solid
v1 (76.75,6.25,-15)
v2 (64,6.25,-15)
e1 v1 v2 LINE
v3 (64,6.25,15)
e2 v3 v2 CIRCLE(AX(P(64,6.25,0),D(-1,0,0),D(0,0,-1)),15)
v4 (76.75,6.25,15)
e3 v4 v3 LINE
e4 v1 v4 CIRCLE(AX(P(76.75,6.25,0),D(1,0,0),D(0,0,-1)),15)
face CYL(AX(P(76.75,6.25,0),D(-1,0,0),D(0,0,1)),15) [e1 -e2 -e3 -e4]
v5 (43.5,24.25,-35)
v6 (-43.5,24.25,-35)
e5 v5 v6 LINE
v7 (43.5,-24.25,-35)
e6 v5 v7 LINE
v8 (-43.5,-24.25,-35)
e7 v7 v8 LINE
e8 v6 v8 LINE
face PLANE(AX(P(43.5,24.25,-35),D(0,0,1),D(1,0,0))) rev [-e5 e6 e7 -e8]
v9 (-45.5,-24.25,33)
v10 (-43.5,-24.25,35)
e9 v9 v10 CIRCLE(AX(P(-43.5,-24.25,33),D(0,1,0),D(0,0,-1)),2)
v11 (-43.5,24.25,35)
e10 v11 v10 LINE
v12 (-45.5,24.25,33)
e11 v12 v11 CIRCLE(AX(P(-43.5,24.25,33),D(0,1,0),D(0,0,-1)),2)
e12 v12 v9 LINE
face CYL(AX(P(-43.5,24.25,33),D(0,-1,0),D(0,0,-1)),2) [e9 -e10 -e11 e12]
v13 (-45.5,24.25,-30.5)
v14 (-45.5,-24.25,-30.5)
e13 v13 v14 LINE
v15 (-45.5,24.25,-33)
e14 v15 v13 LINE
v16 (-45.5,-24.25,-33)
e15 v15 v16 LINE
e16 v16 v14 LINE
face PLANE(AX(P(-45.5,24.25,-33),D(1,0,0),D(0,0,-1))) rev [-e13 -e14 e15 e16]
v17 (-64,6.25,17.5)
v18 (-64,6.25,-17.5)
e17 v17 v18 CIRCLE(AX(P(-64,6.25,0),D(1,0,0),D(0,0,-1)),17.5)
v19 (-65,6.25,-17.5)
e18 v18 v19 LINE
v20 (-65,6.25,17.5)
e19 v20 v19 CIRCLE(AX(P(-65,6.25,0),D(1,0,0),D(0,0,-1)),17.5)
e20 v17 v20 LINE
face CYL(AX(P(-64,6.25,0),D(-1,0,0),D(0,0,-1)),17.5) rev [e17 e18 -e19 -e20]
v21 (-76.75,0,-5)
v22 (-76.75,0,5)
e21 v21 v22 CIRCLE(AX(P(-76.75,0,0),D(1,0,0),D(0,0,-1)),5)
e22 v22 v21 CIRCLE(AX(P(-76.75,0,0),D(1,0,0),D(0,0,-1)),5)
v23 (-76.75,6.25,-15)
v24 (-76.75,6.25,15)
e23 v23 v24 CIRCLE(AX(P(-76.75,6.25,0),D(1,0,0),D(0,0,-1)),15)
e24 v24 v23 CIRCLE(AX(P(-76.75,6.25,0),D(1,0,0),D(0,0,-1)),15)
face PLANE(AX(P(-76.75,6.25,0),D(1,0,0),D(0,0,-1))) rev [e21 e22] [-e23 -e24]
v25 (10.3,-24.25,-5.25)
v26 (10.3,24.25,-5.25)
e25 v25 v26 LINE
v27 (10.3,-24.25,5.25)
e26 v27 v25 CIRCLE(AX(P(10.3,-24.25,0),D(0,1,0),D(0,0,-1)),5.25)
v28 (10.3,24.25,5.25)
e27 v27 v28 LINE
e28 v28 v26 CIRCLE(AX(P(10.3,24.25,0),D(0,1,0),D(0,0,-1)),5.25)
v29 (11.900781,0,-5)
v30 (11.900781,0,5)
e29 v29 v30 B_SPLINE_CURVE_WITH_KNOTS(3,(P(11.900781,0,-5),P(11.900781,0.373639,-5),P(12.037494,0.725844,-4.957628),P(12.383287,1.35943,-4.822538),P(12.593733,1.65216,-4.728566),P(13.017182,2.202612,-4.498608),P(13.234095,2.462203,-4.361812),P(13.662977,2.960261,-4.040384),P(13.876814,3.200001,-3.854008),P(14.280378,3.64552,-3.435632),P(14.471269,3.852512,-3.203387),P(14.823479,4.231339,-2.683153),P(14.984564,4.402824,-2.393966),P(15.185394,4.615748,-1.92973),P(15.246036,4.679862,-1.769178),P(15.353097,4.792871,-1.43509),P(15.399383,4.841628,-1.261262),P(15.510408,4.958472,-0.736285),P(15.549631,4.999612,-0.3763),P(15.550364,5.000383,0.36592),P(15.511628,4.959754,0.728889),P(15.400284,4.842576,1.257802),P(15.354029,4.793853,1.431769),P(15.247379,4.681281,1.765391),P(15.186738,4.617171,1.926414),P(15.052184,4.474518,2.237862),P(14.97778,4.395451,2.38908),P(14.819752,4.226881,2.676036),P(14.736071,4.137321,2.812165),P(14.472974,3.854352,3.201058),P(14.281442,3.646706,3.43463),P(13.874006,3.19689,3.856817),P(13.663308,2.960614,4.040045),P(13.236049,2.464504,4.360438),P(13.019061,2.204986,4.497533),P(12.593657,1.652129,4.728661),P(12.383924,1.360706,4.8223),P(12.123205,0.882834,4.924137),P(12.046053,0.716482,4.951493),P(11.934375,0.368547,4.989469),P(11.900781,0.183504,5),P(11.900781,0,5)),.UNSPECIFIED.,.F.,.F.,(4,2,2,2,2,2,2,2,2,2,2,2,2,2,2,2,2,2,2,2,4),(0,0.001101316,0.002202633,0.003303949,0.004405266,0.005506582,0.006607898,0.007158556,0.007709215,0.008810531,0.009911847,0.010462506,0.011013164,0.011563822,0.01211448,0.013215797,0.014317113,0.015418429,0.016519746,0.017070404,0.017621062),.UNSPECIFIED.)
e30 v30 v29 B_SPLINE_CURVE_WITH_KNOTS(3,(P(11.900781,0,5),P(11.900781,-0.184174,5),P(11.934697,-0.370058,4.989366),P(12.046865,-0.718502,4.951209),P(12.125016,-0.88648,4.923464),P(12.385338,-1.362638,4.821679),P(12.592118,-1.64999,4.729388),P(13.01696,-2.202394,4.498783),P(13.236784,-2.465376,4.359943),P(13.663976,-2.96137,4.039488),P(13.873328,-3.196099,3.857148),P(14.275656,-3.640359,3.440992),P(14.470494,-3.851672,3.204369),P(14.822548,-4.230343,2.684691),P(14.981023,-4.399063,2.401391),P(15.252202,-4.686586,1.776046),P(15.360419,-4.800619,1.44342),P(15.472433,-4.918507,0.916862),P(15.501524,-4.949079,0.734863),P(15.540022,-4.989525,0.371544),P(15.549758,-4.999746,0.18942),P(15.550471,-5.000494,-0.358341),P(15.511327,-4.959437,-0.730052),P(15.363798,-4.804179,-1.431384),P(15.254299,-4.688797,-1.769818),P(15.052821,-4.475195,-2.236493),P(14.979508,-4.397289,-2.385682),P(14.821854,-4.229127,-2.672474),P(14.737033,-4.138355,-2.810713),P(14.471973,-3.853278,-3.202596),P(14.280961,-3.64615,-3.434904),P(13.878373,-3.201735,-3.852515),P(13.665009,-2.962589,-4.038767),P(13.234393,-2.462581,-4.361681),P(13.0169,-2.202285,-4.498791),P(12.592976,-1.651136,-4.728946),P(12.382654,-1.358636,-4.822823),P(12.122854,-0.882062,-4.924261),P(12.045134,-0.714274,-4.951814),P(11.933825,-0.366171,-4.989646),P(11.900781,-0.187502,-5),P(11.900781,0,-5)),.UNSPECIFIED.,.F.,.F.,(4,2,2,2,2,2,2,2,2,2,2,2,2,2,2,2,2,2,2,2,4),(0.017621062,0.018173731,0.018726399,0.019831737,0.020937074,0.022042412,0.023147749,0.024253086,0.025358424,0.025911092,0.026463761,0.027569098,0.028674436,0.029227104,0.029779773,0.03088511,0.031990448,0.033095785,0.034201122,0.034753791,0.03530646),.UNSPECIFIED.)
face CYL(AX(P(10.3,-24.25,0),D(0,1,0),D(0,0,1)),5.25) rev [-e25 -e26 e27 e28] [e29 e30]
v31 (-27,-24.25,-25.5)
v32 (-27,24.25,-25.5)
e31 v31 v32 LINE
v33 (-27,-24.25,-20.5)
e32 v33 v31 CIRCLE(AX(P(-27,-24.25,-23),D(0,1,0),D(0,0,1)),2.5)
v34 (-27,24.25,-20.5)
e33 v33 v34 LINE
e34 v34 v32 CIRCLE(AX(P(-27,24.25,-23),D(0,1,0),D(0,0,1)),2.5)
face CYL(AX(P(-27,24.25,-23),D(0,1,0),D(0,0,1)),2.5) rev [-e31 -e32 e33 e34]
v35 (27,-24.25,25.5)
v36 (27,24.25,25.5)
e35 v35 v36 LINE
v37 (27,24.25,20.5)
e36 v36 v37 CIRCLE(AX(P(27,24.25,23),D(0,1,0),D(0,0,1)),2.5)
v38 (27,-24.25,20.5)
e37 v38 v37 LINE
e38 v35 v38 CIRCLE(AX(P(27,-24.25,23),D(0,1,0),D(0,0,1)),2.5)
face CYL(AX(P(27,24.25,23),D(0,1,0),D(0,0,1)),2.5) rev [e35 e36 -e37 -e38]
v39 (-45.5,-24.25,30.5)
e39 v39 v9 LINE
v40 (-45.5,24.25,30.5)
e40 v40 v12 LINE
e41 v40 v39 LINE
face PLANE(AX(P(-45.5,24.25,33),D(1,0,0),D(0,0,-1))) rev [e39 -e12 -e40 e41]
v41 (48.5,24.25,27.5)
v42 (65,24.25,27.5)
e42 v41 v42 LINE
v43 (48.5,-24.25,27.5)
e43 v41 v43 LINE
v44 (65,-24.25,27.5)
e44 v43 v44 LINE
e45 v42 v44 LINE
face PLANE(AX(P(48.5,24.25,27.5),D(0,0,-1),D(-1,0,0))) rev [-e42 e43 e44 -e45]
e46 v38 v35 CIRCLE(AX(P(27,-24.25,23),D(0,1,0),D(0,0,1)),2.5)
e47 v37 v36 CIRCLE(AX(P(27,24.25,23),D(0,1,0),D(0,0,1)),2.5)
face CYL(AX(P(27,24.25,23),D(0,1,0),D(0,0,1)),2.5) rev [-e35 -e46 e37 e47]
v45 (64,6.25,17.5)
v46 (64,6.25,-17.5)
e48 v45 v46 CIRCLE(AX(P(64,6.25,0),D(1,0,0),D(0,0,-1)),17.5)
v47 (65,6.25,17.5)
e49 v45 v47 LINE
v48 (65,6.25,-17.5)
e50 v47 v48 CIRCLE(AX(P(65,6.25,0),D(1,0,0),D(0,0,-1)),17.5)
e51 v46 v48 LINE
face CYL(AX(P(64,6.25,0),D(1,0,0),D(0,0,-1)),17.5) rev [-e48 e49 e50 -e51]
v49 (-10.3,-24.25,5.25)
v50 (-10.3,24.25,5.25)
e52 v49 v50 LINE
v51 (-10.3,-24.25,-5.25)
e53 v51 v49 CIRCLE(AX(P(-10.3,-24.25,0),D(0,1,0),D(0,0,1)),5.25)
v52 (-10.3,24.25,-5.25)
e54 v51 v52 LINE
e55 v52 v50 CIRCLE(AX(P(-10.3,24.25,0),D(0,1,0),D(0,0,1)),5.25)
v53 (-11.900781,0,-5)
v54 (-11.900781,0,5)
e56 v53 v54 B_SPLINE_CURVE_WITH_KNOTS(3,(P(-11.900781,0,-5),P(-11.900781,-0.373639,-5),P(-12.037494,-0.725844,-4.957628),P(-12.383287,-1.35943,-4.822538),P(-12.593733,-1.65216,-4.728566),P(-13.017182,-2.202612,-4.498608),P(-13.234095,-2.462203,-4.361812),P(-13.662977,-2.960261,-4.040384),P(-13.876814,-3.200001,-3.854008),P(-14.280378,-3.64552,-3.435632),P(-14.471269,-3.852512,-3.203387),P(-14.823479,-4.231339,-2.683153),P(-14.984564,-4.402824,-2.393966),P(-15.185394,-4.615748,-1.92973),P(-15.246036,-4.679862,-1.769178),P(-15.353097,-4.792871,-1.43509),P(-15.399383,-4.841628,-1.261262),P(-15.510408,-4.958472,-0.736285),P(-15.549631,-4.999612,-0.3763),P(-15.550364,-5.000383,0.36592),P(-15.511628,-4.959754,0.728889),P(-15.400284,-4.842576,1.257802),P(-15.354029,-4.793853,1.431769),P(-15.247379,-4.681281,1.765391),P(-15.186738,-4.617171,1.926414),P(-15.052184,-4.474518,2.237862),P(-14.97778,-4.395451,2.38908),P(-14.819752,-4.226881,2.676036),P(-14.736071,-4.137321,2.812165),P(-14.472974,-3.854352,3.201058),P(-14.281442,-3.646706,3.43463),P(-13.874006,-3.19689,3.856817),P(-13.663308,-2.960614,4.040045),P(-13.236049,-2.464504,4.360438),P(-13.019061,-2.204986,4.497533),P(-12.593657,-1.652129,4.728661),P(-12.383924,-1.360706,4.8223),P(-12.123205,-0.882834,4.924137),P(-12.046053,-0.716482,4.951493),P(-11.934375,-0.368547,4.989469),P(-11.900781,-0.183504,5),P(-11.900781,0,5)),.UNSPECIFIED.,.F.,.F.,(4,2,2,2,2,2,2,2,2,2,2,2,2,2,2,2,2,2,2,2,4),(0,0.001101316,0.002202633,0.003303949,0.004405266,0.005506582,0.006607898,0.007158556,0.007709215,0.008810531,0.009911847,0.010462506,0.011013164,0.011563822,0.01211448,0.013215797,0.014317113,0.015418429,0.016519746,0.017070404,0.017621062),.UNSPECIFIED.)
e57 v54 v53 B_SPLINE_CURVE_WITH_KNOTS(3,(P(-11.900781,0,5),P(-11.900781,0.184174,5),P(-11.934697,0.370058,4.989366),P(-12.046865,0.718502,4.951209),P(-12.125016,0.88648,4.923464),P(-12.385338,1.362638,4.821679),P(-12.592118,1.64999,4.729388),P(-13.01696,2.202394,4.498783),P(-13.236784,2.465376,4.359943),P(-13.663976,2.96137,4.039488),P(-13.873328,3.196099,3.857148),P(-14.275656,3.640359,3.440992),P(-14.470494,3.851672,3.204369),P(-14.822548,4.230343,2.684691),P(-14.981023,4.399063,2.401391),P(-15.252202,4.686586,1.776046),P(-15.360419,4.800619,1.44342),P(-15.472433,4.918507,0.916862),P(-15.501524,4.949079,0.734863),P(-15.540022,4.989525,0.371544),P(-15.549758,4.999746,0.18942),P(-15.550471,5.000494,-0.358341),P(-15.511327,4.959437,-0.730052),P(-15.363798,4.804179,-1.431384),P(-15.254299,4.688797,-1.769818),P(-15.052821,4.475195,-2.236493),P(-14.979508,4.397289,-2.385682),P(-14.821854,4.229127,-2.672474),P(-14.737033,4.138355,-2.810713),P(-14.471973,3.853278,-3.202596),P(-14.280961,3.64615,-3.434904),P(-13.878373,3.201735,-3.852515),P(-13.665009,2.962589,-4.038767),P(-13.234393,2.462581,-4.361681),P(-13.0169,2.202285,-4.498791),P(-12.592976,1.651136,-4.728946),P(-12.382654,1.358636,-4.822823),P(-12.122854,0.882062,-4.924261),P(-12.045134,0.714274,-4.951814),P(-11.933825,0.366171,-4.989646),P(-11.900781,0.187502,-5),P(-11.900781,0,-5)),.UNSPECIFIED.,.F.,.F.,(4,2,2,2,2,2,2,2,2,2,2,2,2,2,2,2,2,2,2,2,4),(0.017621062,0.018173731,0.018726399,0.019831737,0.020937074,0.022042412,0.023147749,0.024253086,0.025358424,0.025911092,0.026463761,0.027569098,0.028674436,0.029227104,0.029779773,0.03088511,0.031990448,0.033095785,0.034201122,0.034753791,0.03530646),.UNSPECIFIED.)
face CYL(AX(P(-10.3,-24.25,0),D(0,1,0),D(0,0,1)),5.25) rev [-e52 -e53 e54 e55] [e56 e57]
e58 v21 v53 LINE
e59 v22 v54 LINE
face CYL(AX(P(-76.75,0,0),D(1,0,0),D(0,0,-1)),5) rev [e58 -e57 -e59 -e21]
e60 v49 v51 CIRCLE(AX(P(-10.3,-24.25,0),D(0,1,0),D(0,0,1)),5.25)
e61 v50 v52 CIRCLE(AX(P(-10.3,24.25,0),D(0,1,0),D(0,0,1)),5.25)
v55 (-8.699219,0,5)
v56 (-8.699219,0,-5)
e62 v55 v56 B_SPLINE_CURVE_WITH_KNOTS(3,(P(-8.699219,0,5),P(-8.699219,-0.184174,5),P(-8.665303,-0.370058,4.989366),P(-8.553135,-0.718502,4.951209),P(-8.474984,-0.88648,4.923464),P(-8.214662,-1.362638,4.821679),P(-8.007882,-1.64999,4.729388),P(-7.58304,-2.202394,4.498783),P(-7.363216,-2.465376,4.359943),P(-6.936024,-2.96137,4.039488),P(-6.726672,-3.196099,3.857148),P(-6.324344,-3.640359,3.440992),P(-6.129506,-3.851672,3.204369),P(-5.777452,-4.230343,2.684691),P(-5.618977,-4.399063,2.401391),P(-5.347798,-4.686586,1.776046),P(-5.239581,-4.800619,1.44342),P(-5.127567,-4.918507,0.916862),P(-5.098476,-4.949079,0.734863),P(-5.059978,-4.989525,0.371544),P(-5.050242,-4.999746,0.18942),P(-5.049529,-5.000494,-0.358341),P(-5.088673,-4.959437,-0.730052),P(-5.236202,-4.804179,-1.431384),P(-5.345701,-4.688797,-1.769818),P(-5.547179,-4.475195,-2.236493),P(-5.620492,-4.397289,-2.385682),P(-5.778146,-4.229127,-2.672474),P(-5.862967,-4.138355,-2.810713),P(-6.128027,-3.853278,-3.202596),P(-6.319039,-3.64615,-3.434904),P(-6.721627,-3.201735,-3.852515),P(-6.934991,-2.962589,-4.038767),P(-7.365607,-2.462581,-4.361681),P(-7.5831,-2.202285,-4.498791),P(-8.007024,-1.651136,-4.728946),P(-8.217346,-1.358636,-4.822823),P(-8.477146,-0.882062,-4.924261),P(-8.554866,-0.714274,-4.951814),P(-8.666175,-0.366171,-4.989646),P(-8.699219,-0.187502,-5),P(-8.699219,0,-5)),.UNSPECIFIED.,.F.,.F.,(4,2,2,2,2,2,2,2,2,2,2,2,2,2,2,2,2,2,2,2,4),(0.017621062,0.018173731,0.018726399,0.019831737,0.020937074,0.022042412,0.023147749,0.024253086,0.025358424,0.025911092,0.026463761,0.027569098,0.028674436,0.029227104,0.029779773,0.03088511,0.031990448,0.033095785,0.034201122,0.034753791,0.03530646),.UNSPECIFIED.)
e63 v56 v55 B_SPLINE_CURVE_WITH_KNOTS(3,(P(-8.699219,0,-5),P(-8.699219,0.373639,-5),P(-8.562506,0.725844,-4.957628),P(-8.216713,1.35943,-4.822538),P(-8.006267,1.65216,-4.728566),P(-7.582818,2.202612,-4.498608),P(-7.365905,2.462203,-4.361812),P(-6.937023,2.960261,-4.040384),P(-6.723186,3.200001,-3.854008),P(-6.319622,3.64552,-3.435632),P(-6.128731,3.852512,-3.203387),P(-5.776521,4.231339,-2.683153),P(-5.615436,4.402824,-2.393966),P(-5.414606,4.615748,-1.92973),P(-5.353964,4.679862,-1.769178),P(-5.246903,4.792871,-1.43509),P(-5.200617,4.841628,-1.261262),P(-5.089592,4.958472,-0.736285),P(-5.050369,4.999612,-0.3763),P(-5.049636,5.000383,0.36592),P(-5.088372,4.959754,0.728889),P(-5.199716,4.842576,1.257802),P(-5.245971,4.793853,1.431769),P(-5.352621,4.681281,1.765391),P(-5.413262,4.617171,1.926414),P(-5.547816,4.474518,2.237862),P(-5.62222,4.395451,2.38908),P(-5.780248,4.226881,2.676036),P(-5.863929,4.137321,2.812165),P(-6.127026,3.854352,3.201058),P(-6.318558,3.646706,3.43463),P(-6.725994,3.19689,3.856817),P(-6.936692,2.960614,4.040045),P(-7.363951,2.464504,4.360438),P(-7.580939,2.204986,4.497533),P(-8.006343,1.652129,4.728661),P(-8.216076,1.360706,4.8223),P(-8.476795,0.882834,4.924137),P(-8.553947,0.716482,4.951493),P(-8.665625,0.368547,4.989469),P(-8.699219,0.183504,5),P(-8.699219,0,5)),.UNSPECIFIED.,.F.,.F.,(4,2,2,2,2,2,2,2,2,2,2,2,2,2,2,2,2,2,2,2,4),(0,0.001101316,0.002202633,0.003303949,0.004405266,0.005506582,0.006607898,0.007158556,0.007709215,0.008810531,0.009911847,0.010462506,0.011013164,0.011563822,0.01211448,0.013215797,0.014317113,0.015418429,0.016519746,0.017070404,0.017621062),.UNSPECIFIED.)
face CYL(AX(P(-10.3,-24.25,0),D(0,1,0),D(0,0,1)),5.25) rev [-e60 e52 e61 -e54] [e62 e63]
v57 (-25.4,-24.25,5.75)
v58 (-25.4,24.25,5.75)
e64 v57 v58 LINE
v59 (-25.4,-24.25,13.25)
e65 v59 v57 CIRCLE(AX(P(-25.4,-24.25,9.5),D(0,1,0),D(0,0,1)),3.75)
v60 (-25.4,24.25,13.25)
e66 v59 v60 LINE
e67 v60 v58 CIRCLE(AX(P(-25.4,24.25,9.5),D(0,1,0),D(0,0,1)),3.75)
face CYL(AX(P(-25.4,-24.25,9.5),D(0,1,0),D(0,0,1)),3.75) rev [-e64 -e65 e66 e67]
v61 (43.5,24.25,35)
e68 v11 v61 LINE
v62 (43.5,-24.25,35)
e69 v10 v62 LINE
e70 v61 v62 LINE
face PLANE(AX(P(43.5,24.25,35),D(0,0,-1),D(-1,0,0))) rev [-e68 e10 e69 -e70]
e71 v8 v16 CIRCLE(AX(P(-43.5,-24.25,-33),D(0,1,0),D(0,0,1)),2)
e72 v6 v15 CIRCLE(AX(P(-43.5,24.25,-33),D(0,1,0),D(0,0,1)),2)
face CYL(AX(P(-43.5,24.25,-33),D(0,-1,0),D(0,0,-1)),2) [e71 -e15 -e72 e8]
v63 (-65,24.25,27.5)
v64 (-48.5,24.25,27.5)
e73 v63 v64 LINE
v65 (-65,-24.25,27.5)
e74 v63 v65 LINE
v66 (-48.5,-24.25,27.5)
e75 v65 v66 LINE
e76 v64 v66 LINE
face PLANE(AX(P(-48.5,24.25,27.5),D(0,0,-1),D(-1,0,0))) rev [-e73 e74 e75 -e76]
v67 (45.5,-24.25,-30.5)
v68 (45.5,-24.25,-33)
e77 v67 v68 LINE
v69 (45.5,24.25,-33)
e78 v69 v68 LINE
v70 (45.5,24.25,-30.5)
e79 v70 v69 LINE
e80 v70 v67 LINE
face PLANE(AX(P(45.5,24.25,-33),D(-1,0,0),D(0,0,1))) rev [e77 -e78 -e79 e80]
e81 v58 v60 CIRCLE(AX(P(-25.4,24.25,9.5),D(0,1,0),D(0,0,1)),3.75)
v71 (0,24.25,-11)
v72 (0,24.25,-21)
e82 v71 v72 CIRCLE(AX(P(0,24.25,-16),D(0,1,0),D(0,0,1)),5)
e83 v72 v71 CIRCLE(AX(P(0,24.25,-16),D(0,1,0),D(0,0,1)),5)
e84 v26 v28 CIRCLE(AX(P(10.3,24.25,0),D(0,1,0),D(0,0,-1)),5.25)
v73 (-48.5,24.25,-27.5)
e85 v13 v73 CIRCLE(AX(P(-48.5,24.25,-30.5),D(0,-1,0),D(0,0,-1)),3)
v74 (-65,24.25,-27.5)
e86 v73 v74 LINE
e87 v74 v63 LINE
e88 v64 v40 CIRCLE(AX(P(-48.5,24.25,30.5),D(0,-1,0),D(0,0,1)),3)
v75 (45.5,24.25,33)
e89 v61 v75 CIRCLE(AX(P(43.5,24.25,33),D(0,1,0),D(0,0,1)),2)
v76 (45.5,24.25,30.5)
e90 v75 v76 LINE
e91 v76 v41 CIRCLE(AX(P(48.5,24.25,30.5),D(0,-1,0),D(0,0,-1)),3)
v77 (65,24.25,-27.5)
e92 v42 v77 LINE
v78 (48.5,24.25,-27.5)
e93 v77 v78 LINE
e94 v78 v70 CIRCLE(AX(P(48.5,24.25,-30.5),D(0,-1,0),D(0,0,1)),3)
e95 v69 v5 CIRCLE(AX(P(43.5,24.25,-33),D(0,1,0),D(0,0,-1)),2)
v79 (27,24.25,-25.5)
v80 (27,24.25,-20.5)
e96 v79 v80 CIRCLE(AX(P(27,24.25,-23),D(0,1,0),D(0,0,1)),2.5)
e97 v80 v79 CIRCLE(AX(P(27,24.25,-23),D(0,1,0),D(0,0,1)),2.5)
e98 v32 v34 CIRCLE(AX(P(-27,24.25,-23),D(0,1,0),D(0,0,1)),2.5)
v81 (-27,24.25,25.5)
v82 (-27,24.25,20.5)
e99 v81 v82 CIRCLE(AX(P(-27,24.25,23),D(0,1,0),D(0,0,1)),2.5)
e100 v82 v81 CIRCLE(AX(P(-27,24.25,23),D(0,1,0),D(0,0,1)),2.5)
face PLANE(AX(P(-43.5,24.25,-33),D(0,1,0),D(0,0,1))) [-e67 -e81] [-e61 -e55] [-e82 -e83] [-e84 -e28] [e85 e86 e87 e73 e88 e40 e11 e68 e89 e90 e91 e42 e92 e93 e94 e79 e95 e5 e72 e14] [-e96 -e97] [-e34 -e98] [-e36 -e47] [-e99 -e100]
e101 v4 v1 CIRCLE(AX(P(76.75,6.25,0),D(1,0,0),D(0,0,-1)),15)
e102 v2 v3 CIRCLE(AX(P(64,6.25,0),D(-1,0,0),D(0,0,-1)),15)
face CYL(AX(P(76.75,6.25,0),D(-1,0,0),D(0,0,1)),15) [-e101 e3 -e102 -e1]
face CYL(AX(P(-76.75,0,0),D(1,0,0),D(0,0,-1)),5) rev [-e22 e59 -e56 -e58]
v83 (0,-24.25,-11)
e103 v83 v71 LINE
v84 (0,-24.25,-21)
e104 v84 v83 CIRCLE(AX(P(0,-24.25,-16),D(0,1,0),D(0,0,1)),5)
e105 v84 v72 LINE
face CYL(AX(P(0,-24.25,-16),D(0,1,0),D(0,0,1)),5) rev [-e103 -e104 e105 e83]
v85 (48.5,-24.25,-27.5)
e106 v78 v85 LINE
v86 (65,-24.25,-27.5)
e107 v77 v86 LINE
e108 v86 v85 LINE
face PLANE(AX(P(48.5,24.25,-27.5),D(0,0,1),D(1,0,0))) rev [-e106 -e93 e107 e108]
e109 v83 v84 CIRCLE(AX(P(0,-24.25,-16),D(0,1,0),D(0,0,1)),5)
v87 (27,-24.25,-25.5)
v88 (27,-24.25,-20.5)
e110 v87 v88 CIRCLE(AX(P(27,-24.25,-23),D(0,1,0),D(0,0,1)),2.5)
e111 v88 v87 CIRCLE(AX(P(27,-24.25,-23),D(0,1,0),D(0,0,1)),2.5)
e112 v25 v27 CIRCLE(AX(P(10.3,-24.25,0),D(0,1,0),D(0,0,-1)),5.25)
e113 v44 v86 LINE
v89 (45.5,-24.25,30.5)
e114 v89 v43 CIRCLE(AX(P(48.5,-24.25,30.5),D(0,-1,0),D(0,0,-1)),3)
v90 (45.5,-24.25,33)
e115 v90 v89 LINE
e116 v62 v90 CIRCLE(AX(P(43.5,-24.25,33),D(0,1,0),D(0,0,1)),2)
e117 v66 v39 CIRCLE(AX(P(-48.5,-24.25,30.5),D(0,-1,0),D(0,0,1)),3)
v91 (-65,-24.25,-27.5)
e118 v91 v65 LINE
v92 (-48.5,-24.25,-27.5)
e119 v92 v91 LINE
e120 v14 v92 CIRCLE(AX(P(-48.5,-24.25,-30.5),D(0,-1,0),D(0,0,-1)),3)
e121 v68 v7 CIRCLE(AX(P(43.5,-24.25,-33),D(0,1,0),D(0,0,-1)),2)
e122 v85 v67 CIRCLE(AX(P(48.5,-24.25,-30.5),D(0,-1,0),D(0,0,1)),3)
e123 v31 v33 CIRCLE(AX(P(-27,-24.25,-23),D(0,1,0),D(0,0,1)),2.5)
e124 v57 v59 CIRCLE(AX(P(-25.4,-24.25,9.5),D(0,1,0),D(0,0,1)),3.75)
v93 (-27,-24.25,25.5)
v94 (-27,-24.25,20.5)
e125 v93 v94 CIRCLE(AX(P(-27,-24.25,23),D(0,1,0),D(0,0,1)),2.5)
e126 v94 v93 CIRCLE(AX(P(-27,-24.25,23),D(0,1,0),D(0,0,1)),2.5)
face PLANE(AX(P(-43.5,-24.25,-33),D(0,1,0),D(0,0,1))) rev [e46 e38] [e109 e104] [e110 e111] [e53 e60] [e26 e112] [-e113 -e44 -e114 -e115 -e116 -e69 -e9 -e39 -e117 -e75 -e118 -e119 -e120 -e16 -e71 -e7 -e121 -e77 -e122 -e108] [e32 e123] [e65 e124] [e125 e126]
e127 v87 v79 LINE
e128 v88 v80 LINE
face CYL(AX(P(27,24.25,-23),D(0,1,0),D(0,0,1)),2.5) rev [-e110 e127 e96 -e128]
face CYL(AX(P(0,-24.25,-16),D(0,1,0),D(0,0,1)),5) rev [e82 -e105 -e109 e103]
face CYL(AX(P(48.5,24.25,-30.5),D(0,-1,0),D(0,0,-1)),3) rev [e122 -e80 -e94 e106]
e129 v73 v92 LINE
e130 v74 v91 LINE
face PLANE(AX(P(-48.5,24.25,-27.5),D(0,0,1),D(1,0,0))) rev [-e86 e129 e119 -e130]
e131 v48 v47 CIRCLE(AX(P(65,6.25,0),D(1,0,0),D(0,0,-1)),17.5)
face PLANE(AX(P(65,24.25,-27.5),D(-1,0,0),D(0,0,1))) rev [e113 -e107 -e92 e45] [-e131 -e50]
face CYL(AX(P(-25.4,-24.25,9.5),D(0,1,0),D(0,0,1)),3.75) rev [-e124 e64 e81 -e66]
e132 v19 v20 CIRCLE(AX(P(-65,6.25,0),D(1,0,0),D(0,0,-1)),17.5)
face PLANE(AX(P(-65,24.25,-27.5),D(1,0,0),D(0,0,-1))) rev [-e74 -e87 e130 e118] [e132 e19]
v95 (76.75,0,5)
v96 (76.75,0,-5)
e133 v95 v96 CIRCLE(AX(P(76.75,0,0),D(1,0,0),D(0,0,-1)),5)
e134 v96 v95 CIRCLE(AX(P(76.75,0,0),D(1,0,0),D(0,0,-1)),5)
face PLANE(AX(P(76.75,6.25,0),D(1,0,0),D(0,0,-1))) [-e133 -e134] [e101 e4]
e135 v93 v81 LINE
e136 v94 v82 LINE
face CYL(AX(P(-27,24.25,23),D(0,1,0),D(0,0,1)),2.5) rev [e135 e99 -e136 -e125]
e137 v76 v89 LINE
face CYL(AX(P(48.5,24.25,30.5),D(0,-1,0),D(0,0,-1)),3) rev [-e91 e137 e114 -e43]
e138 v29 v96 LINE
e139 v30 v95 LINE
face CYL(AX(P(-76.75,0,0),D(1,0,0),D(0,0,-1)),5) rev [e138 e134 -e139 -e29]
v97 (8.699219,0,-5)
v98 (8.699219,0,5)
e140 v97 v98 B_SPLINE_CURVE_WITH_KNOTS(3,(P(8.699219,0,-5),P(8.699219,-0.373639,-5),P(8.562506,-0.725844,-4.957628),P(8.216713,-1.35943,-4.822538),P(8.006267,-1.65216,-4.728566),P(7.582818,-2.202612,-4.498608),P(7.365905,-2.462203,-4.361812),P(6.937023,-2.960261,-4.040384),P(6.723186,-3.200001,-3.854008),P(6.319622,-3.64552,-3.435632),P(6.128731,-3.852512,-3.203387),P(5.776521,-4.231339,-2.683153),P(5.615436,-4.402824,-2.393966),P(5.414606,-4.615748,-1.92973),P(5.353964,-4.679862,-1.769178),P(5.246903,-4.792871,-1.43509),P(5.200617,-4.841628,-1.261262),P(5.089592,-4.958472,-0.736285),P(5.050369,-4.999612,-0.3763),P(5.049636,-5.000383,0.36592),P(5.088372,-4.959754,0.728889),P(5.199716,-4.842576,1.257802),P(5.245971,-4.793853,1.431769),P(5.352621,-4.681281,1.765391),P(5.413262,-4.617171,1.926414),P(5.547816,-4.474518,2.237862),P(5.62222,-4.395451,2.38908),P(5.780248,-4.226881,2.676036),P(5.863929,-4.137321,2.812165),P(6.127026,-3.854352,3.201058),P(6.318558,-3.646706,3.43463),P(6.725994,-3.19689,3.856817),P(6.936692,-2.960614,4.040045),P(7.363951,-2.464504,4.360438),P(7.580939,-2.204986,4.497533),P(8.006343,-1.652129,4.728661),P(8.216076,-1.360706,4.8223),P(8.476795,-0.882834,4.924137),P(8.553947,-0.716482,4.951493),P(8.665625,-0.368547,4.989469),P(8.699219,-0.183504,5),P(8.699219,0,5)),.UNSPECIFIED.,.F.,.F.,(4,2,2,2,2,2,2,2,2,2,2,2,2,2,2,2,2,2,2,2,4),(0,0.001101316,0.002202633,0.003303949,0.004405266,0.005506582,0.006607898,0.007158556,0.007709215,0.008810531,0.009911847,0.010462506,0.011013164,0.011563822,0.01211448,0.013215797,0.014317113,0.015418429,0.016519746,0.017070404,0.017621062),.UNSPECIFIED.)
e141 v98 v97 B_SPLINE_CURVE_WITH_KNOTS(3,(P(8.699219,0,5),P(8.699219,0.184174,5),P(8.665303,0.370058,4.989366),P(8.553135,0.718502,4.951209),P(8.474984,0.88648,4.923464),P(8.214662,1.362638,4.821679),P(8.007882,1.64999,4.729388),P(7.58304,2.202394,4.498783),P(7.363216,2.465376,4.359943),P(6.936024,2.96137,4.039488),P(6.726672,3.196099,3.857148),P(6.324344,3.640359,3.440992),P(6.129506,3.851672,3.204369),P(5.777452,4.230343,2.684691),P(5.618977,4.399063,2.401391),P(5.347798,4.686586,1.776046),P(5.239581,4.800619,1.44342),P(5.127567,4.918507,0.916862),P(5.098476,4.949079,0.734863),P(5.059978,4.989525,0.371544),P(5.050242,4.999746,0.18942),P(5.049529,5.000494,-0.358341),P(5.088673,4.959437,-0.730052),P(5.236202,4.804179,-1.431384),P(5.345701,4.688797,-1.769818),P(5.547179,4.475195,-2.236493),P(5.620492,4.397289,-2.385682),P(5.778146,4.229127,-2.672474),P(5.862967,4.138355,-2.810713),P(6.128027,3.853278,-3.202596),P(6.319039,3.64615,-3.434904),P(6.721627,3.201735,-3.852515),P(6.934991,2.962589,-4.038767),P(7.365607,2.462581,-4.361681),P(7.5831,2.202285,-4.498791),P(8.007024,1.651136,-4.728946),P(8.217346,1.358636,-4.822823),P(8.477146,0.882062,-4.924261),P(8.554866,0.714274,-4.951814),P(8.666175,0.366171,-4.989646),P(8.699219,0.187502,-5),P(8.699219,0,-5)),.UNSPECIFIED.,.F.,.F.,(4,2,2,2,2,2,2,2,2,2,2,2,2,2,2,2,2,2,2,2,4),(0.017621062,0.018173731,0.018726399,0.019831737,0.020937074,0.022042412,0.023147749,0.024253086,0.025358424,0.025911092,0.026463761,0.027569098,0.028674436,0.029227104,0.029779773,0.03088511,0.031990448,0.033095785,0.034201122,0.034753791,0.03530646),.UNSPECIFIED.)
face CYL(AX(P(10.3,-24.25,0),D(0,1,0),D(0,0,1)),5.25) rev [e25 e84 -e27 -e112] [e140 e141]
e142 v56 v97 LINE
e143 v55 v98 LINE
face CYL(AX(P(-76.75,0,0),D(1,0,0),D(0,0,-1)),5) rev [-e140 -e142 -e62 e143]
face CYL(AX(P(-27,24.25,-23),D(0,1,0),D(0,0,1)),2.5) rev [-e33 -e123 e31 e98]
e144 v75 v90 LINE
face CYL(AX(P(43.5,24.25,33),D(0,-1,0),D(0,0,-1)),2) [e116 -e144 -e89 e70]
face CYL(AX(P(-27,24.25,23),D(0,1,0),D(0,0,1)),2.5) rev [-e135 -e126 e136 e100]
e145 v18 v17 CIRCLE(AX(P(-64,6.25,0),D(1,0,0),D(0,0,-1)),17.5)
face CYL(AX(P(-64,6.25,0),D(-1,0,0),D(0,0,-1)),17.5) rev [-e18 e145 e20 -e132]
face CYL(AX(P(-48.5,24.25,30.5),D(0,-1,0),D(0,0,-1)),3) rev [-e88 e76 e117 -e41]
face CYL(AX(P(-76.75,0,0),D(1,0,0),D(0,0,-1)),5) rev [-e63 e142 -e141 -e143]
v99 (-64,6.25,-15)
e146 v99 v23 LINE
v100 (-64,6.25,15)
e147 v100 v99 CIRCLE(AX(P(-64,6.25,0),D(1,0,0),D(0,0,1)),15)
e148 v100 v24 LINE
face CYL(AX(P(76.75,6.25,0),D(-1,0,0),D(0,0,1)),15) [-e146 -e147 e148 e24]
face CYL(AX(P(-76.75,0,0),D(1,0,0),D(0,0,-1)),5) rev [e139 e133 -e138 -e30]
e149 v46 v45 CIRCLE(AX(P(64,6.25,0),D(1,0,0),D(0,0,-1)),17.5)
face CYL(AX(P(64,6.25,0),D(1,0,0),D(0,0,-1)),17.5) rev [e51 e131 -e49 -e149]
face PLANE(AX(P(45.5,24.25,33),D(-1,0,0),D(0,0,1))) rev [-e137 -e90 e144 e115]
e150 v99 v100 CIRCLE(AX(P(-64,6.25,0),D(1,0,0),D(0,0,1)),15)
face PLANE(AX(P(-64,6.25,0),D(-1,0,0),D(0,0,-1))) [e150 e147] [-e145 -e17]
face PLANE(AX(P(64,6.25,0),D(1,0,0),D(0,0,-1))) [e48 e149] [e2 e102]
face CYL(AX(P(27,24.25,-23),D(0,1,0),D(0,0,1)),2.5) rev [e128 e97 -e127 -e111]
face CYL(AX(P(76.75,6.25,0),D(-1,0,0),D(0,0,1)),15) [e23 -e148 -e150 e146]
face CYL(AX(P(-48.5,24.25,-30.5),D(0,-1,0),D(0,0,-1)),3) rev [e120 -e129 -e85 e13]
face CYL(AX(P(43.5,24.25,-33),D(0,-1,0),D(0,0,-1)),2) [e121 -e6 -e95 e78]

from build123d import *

# Parameters (mm, degrees)
BOSS_EXTRUDE_1_DEPTH = 24.25
SKETCH_2_R           = 17.5
CUT_EXTRUDE_3_DEPTH  = 1
SKETCH_3_R           = 15
BOSS_EXTRUDE_3_DEPTH = 76.75
SKETCH_4_R           = 5
SKETCH_4_R_2         = 5.25
SKETCH_4_R_3         = 3.75
CUT_EXTRUDE_1_DEPTH  = 98.302684958
M6_THREADED_HOLE_1_D = 5
SKETCH_5_R           = 5
CUT_EXTRUDE_2_DEPTH  = 160.2963041


with BuildPart() as part:
    # Sketch 1 → Boss-Extrude 1 (new, symmetric)
    with BuildSketch(Plane(origin=(0, 0, 0), x_dir=(1, 0, 0), z_dir=(0, 1, 0))):
        with BuildLine():
            Line((43.5, 35), (-43.5, 35))
            ThreePointArc((-43.5, 35), (-44.914213562, 34.414213562), (-45.5, 33))
            Line((-45.5, 33), (-45.5, 30.5))
            ThreePointArc((-45.5, 30.5), (-46.378679656, 28.378679656), (-48.5, 27.5))
            Line((-48.5, 27.5), (-65, 27.5))
            Line((-65, 27.5), (-65, -27.5))
            Line((-65, -27.5), (-48.5, -27.5))
            ThreePointArc((-48.5, -27.5), (-46.378679656, -28.378679656), (-45.5, -30.5))
            Line((-45.5, -30.5), (-45.5, -33))
            ThreePointArc((-45.5, -33), (-44.914213562, -34.414213562), (-43.5, -35))
            Line((-43.5, -35), (43.5, -35))
            ThreePointArc((43.5, -35), (44.914213562, -34.414213562), (45.5, -33))
            Line((45.5, -33), (45.5, -30.5))
            ThreePointArc((45.5, -30.5), (46.378679656, -28.378679656), (48.5, -27.5))
            Line((48.5, -27.5), (65, -27.5))
            Line((65, -27.5), (65, 27.5))
            Line((65, 27.5), (48.5, 27.5))
            ThreePointArc((48.5, 27.5), (46.378679656, 28.378679656), (45.5, 30.5))
            Line((45.5, 30.5), (45.5, 33))
            ThreePointArc((45.5, 33), (44.914213562, 34.414213562), (43.5, 35))
        make_face()
    extrude(amount=BOSS_EXTRUDE_1_DEPTH, both=True)

    # Sketch 2 → Cut-Extrude 3 (cut)
    with BuildSketch(Plane(origin=(65, 0, 0), x_dir=(0, 0, -1), z_dir=(1, 0, 0))):
        with Locations((0, 6.25)):
            Circle(SKETCH_2_R)
    cut_extrude_3 = extrude(amount=-CUT_EXTRUDE_3_DEPTH, mode=Mode.SUBTRACT)

    # Mirror 1: Cut-Extrude 3 across plane
    add(cut_extrude_3.mirror(Plane(origin=(0, 0, 0), x_dir=(0, 0, 1), z_dir=(1, 0, 0))), mode=Mode.SUBTRACT)

    # Sketch 3 → Boss-Extrude 3 (add, symmetric)
    with BuildSketch(Plane(origin=(0, 0, 0), x_dir=(0, 0, -1), z_dir=(1, 0, 0))):
        with Locations(Location((0, 6.25, 0), (0, 0, 180))):
            Circle(SKETCH_3_R)
    extrude(amount=BOSS_EXTRUDE_3_DEPTH, both=True)

    # Sketch 4 → Cut-Extrude 1 (cut, through all)
    with BuildSketch(Plane(origin=(0, 24.25, 0), x_dir=(1, 0, 0), z_dir=(0, 1, 0))):
        with Locations(Location((0, 16, 0), (0, 0, 270))):
            Circle(SKETCH_4_R)
        with Locations(Location((-10.3, 0, 0), (0, 0, 270))):
            Circle(SKETCH_4_R_2)
        with Locations(Location((-25.4, -9.5, 0), (0, 0, 270))):
            Circle(SKETCH_4_R_3)
        with Locations(Location((10.3, 0, 0), (0, 0, 270))):
            Circle(SKETCH_4_R_2)
    extrude(amount=-CUT_EXTRUDE_1_DEPTH, mode=Mode.SUBTRACT)

    # M6 threaded hole 1 (through all)
    with Locations(Plane(origin=(-27, 24.25, -23), x_dir=(0, 0, 1), z_dir=(0, 1, 0))):
        with Locations((0, 0), (0, 54), (46, 54), (46, 0)):
            Hole(M6_THREADED_HOLE_1_D / 2)

    # Sketch 5 → Cut-Extrude 2 (cut, through all)
    with BuildSketch(Plane(origin=(76.75, 0, 0), x_dir=(0, 0, -1), z_dir=(1, 0, 0))):
        Circle(SKETCH_5_R)
    extrude(amount=-CUT_EXTRUDE_2_DEPTH, mode=Mode.SUBTRACT)


solid = part.part
